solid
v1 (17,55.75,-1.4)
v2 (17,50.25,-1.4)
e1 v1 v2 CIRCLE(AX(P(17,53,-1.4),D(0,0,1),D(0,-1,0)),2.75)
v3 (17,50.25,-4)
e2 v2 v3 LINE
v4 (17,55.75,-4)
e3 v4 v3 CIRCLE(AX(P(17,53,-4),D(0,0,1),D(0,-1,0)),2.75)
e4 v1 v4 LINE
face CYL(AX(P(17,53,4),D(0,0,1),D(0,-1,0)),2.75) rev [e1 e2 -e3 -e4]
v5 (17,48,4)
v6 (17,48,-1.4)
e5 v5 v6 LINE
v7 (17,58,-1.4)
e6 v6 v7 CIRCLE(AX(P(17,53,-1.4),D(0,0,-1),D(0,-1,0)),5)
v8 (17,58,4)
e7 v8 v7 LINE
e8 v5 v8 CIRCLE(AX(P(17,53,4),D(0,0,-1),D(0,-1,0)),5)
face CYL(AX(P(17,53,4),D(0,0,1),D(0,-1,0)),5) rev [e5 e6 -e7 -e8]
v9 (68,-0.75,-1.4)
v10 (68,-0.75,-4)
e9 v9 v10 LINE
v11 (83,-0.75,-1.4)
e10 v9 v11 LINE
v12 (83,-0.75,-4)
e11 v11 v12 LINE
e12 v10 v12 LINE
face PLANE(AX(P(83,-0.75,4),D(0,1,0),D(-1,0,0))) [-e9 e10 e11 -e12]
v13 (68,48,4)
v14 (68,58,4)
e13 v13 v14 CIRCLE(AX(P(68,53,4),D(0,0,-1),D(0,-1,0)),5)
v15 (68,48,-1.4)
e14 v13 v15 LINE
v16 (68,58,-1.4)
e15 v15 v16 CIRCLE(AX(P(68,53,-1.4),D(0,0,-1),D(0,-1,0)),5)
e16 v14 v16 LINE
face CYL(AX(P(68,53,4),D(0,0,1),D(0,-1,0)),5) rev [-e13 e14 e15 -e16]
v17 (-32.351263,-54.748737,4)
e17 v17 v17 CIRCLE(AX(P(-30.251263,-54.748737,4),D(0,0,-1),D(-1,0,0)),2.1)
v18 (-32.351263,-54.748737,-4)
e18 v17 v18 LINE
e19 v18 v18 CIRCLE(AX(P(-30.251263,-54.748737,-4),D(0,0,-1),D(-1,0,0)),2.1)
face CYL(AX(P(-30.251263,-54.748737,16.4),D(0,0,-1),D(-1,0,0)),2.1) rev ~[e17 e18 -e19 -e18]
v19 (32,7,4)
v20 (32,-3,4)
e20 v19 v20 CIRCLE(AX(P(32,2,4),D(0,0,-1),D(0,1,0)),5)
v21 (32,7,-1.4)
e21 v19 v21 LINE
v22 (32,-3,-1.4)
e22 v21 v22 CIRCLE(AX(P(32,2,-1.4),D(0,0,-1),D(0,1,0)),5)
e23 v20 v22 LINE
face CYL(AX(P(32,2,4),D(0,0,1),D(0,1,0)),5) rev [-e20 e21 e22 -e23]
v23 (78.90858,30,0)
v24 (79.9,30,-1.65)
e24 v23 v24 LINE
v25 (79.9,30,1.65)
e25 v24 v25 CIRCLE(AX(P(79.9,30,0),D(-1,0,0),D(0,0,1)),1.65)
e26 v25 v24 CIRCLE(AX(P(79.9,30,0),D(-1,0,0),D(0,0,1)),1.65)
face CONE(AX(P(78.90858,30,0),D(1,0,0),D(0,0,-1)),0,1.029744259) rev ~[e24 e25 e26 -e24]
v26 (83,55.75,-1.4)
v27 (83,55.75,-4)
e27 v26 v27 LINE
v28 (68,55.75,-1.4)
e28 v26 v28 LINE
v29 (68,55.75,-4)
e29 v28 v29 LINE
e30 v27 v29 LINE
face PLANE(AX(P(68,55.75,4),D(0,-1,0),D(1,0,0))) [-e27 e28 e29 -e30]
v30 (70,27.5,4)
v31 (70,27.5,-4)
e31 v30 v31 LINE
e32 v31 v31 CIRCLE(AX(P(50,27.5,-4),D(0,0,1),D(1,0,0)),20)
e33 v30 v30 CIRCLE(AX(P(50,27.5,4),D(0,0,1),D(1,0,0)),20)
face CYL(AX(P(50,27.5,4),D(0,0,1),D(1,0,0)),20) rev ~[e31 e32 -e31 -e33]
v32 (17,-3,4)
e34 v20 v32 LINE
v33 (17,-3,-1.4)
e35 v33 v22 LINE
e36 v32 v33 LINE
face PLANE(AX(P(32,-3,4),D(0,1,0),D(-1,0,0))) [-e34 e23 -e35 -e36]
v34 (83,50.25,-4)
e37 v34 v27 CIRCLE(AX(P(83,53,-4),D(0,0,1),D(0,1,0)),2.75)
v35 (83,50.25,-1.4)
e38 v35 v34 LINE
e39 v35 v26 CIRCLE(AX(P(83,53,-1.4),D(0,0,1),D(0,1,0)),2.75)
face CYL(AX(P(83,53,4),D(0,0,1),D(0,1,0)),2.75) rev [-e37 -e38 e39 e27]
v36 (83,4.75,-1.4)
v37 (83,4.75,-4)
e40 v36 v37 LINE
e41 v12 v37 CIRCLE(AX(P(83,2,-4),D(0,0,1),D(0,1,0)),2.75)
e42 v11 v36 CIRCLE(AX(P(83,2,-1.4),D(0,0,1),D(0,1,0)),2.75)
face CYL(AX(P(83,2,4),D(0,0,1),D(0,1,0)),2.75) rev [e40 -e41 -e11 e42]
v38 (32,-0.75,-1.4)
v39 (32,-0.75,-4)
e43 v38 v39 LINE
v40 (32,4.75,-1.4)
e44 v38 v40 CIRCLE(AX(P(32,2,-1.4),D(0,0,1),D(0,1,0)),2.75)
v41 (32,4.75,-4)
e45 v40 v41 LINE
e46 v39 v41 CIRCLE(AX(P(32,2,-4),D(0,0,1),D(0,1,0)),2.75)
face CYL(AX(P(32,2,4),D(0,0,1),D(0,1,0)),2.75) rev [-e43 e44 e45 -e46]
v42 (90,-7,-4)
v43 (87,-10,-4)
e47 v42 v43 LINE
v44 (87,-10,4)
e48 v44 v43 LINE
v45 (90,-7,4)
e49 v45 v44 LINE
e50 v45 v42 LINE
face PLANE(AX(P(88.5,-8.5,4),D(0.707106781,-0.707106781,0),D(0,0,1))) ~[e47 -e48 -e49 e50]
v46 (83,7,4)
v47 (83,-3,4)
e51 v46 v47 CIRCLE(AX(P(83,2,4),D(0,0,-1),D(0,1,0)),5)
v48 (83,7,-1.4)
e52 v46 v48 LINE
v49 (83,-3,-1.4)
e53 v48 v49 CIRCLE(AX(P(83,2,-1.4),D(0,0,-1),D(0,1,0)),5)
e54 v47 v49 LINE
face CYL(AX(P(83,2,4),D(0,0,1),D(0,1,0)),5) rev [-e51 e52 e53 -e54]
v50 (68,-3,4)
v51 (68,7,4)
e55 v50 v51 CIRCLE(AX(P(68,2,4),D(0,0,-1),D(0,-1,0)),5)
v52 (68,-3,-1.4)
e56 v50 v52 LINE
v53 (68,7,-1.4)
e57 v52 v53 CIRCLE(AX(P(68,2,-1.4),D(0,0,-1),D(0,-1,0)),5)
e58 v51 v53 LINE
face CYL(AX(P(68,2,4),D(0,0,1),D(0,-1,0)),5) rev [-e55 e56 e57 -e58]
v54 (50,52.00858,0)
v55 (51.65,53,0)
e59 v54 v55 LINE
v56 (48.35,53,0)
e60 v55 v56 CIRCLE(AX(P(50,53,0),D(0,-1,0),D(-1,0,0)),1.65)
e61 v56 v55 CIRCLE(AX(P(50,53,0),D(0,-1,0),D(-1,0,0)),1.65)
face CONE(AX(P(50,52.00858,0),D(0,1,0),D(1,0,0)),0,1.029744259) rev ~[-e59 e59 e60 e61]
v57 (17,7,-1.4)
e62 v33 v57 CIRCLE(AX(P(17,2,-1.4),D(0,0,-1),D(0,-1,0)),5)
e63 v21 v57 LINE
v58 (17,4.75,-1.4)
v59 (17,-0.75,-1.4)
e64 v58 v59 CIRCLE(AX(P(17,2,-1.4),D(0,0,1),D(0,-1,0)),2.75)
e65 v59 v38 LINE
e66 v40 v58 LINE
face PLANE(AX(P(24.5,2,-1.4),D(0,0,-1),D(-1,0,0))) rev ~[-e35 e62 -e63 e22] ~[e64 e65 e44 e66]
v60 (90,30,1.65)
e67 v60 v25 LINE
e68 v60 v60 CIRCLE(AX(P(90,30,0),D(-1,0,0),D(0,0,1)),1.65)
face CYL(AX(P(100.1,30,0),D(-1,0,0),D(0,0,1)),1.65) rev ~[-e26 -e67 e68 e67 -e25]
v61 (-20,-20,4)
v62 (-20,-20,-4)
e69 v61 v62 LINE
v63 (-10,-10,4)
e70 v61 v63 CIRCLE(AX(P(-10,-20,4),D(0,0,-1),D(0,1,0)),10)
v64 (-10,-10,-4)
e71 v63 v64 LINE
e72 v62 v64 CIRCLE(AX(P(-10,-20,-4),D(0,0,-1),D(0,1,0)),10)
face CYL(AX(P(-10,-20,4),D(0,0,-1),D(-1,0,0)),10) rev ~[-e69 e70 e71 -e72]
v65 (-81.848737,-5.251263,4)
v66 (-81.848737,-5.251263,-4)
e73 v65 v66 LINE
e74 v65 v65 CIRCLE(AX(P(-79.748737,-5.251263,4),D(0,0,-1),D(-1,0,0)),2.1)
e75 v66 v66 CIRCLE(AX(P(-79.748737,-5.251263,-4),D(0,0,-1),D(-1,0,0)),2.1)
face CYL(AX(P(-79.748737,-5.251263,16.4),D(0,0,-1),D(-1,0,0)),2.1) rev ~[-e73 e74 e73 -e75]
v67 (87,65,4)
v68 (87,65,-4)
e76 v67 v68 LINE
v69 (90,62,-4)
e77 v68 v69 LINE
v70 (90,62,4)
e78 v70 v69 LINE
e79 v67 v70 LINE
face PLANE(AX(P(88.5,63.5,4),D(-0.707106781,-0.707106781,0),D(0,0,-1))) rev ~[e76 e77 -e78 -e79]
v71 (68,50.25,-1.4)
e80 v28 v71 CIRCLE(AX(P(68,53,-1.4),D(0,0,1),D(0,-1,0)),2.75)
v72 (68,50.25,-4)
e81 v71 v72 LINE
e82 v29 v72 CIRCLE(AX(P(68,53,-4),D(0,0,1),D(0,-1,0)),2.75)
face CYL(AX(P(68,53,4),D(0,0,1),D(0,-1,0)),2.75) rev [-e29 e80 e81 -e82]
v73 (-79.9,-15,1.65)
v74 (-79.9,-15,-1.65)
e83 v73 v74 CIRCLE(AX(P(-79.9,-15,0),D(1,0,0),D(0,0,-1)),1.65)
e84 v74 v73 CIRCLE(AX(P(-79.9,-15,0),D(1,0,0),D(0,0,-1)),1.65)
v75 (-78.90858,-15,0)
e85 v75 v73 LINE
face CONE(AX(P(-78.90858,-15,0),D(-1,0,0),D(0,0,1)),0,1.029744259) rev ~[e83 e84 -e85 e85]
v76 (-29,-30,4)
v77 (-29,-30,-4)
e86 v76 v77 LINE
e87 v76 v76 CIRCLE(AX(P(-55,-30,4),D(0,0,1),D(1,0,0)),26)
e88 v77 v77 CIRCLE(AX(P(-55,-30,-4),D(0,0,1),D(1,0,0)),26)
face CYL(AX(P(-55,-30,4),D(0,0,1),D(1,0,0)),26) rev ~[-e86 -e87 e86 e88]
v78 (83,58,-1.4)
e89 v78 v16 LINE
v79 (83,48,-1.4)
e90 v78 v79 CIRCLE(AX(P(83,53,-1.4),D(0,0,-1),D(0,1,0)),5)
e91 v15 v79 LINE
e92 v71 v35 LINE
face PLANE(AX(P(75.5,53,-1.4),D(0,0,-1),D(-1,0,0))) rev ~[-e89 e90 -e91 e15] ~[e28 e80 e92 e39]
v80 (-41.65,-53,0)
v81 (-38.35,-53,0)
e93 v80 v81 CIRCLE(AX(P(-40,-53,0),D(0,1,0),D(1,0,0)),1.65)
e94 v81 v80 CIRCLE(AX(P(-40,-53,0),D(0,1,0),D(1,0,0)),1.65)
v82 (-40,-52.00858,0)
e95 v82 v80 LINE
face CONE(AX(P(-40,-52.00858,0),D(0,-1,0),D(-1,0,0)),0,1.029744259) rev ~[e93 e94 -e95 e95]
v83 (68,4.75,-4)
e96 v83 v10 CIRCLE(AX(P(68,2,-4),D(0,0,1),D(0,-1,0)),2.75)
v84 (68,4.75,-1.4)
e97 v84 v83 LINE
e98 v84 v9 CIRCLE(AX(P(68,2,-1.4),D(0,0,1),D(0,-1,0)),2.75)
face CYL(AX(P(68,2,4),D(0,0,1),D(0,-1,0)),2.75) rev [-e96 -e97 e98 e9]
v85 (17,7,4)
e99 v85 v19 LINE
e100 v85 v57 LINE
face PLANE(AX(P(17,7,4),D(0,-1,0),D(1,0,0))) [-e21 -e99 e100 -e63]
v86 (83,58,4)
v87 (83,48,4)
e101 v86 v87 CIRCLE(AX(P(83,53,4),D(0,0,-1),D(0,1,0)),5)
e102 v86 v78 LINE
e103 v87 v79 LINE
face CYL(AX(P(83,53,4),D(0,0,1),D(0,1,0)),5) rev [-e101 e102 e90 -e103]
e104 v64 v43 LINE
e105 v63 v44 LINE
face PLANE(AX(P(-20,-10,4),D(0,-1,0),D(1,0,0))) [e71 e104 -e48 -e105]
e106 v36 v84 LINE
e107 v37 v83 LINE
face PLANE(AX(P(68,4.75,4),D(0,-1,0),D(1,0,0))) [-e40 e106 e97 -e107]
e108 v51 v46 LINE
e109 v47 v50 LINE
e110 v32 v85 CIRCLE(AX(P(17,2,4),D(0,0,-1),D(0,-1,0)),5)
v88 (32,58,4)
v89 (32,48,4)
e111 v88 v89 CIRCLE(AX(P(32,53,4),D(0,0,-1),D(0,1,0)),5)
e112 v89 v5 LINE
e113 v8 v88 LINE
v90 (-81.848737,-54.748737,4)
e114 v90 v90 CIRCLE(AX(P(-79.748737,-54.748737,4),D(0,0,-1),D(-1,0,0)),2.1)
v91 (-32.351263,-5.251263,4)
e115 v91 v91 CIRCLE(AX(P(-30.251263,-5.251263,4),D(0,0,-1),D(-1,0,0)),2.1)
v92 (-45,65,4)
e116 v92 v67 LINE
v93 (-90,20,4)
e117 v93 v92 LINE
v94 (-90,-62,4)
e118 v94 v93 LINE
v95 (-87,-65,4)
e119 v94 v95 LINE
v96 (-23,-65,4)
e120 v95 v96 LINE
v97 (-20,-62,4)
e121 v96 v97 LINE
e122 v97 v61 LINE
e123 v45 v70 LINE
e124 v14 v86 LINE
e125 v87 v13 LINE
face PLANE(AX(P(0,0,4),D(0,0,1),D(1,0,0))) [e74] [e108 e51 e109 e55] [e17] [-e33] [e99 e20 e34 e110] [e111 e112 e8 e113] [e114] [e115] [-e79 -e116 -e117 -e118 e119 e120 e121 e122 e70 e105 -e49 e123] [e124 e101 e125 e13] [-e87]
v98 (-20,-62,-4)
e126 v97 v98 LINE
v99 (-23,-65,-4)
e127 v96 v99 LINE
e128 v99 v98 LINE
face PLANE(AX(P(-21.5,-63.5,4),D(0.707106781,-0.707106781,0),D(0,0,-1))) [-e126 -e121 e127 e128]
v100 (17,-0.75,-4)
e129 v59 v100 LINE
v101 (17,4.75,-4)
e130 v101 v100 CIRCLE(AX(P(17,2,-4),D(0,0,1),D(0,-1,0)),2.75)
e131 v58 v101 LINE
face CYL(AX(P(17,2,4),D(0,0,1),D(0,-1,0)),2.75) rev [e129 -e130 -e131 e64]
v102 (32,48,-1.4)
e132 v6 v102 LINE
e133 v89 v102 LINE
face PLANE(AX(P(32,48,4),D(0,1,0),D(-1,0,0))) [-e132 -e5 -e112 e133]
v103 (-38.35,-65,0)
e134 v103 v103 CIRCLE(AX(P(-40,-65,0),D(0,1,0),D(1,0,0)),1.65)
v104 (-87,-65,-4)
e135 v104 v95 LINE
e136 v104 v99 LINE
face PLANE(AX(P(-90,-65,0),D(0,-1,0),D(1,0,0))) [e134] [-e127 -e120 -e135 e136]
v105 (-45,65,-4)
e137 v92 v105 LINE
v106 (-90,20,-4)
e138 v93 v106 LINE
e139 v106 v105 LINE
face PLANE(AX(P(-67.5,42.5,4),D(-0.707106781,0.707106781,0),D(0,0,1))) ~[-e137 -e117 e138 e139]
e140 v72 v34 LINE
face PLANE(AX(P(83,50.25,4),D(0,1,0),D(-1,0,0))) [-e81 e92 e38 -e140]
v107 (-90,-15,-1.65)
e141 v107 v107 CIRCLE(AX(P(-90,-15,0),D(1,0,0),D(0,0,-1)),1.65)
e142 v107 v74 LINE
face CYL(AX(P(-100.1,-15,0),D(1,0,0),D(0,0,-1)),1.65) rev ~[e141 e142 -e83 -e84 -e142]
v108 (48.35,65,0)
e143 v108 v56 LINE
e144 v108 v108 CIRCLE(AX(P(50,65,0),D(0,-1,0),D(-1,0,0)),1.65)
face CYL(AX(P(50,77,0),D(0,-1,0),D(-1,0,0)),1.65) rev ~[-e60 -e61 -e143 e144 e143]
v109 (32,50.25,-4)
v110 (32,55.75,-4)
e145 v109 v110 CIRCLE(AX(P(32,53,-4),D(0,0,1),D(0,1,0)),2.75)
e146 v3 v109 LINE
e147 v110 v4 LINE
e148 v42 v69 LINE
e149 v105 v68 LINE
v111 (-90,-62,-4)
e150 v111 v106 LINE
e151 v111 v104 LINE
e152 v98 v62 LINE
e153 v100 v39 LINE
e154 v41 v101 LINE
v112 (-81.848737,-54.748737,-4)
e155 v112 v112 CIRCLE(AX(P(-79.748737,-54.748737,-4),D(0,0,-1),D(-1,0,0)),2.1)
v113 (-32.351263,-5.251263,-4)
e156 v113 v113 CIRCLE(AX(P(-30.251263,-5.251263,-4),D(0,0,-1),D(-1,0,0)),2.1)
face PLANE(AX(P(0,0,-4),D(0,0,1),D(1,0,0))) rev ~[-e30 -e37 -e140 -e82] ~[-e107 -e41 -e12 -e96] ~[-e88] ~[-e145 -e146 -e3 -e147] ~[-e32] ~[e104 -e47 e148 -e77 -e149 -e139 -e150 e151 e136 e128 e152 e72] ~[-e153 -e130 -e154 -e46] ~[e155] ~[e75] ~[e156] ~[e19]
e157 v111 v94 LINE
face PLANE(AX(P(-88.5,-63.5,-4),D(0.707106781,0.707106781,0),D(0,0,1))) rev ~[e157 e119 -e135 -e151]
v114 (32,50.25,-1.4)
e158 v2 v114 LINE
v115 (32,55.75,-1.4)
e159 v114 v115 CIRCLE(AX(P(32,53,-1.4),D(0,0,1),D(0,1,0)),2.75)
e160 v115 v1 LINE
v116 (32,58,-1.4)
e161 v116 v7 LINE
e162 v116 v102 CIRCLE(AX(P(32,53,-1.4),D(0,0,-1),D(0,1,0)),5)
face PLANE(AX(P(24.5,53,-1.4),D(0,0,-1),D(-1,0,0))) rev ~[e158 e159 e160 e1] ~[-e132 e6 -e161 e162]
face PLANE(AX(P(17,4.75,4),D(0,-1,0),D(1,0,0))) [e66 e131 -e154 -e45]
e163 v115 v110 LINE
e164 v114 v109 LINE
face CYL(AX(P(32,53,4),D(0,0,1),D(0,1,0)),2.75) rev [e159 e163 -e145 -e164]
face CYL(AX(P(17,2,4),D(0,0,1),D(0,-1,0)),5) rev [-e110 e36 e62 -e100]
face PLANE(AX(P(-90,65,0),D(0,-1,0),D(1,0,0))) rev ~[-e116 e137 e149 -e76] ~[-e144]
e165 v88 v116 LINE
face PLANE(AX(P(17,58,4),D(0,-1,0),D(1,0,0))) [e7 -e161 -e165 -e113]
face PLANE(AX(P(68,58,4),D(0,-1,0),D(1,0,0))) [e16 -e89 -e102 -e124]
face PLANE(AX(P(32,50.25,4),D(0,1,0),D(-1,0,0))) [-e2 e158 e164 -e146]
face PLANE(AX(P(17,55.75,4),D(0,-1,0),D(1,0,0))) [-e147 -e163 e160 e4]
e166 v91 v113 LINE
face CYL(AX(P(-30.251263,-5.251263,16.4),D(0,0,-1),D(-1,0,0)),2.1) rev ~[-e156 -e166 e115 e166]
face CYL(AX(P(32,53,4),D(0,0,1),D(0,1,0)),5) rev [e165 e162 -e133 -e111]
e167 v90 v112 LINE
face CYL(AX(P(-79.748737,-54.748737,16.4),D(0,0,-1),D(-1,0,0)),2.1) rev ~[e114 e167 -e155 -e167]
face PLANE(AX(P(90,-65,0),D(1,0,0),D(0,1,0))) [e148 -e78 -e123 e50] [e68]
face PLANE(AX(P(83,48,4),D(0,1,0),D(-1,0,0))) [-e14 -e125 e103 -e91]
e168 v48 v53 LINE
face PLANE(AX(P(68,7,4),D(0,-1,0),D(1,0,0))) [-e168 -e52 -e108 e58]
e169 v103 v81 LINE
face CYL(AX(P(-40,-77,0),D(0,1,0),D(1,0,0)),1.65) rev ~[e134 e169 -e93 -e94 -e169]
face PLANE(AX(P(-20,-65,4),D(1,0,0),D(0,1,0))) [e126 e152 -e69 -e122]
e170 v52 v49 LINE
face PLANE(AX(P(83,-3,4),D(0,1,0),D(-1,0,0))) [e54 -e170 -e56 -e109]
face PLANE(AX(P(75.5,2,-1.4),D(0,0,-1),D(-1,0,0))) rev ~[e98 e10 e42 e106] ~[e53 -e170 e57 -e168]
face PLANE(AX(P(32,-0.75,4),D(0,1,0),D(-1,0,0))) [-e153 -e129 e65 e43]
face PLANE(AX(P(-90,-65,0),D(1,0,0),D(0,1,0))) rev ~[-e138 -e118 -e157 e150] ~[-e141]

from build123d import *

# Parameters (mm, degrees)
SKETCH_2_W                     = 180
SKETCH_2_H                     = 130
EXTRUDE_1_DEPTH                = 4
SKETCH_3_W                     = 110
SKETCH_3_H                     = 55
CUT_EXTRUDE_1_DEPTH            = 8
SKETCH_4_R                     = 26
CUT_EXTRUDE_2_DEPTH            = 8
HOLE_WIZARD_M5_1_D             = 4.2
HOLE_WIZARD_M5_1_DEPTH         = 12.4
HOLE_WIZARD_M5_1_TIP           = 1.2618073
SKETCH_7_R                     = 20
CUT_EXTRUDE_3_DEPTH            = 8
HOLE_WIZARD_M4_1_D             = 3.3
HOLE_WIZARD_M4_1_DEPTH         = 12
HOLE_WIZARD_M4_1_TIP           = 0.991420021
HOLE_WIZARD_M4_2_D             = 3.3
HOLE_WIZARD_M4_2_DEPTH         = 12
HOLE_WIZARD_M4_2_TIP           = 0.991420021
CHAMFER_1_SIZE                 = 45
CHAMFER_2_SIZE                 = 3
FILLET_1_R                     = 10
HOLE_WIZARD_M5_1_2_D           = 5.5
HOLE_WIZARD_M5_1_2_DEPTH       = 10.1
HOLE_WIZARD_M5_1_2_CBORE_D     = 10
HOLE_WIZARD_M5_1_2_CBORE_DEPTH = 5.4
HOLE_WIZARD_M5_1_2_TIP         = 1.652366702
CUT_EXTRUDE_6_DEPTH            = 112.30588484
CUT_EXTRUDE_7_DEPTH            = 5.4
PATTERN_LINEAR_1_COUNT         = 2
PATTERN_LINEAR_1_PITCH         = 51
PATTERN_LINEAR_1_COUNT_DIR2    = 2
PATTERN_LINEAR_1_PITCH_DIR2    = 51
HOLE_WIZARD_M4_3_D             = 3.3
HOLE_WIZARD_M4_3_DEPTH         = 10.1
HOLE_WIZARD_M4_3_TIP           = 0.991420021
HOLE_WIZARD_M4_4_D             = 3.3
HOLE_WIZARD_M4_4_DEPTH         = 10.1
HOLE_WIZARD_M4_4_TIP           = 0.991420021


with BuildPart() as part:
    # 草图2 → 凸台-拉伸1 (new, symmetric)
    with BuildSketch(Plane.XY):
        Rectangle(SKETCH_2_W, SKETCH_2_H)
    extrude(amount=EXTRUDE_1_DEPTH, both=True)

    # 草图3 → 切除-拉伸1 (cut)
    with BuildSketch(Plane.XY.offset(4)):
        with Locations((35, -37.5)):
            Rectangle(SKETCH_3_W, SKETCH_3_H)
    extrude(amount=-CUT_EXTRUDE_1_DEPTH, mode=Mode.SUBTRACT)

    # 草图4 → 切除-拉伸2 (cut)
    with BuildSketch(Plane.XY.offset(4)):
        with Locations((-55, -30)):
            Circle(SKETCH_4_R)
    extrude(amount=-CUT_EXTRUDE_2_DEPTH, mode=Mode.SUBTRACT)

    # Hole Wizard M5 _1
    with Locations(Plane.XY.offset(4)):
        with Locations((-30.251262658, -54.748737342), (-79.748737342, -5.251262658), (-79.748737342, -54.748737342), (-30.251262658, -5.251262658)):
            Hole(HOLE_WIZARD_M5_1_D / 2, depth=HOLE_WIZARD_M5_1_DEPTH)
            with Locations((0, 0, -(HOLE_WIZARD_M5_1_DEPTH + HOLE_WIZARD_M5_1_TIP / 2))):  # 118° drill point
                Cone(0, HOLE_WIZARD_M5_1_D / 2, HOLE_WIZARD_M5_1_TIP, mode=Mode.SUBTRACT)

    # 草图7 → 切除-拉伸3 (cut)
    with BuildSketch(Plane.XY.offset(4)):
        with Locations((50, 27.5)):
            Circle(SKETCH_7_R)
    extrude(amount=-CUT_EXTRUDE_3_DEPTH, mode=Mode.SUBTRACT)

    # M4 螺纹孔1
    with Locations(Plane(origin=(0, 65, 0), x_dir=(1, 0, 0), z_dir=(0, 1, 0))):
        with Locations((50, 0)):
            Hole(HOLE_WIZARD_M4_1_D / 2, depth=HOLE_WIZARD_M4_1_DEPTH)
            with Locations((0, 0, -(HOLE_WIZARD_M4_1_DEPTH + HOLE_WIZARD_M4_1_TIP / 2))):  # 118° drill point
                Cone(0, HOLE_WIZARD_M4_1_D / 2, HOLE_WIZARD_M4_1_TIP, mode=Mode.SUBTRACT)

    # M4 螺纹孔2
    with Locations(Plane(origin=(0, -65, 0), x_dir=(-1, 0, 0), z_dir=(0, -1, 0))):
        with Locations((40, 0)):
            Hole(HOLE_WIZARD_M4_2_D / 2, depth=HOLE_WIZARD_M4_2_DEPTH)
            with Locations((0, 0, -(HOLE_WIZARD_M4_2_DEPTH + HOLE_WIZARD_M4_2_TIP / 2))):  # 118° drill point
                Cone(0, HOLE_WIZARD_M4_2_D / 2, HOLE_WIZARD_M4_2_TIP, mode=Mode.SUBTRACT)

    # 倒角1
    chamfer_1_edges = [part.edges().sort_by_distance(p)[0] for p in [
        (-90, 65, 0),
    ]]
    chamfer(chamfer_1_edges, length=CHAMFER_1_SIZE)

    # 倒角2
    chamfer_2_edges = [part.edges().sort_by_distance(p)[0] for p in [
        (90, -10, 0),
        (-20, -65, 0),
        (-90, -65, 0),
        (90, 65, 0),
    ]]
    chamfer(chamfer_2_edges, length=CHAMFER_2_SIZE)

    # 圆角1
    fillet_1_edges = [part.edges().sort_by_distance(p)[0] for p in [
        (-20, -10, 0),
    ]]
    fillet(fillet_1_edges, radius=FILLET_1_R)

    # Hole Wizard M5 _1 2
    with Locations(Plane.XY.offset(4)):
        with Locations((24.5, 53), (75.5, 53), (24.5, 2), (75.5, 2)):
            CounterBoreHole(HOLE_WIZARD_M5_1_2_D / 2, HOLE_WIZARD_M5_1_2_CBORE_D / 2, HOLE_WIZARD_M5_1_2_CBORE_DEPTH, depth=HOLE_WIZARD_M5_1_2_DEPTH)
            with Locations((0, 0, -(HOLE_WIZARD_M5_1_2_DEPTH + HOLE_WIZARD_M5_1_2_TIP / 2))):  # 118° drill point
                Cone(0, HOLE_WIZARD_M5_1_2_D / 2, HOLE_WIZARD_M5_1_2_TIP, mode=Mode.SUBTRACT)

    # 草图18 → 切除-拉伸6 (cut, through all)
    with BuildSketch(Plane.XY.offset(4)):
        with BuildLine():
            Line((17, 55.75), (32, 55.75))
            ThreePointArc((32, 55.75), (34.75, 53), (32, 50.25))
            Line((32, 50.25), (17, 50.25))
            ThreePointArc((17, 50.25), (14.25, 53), (17, 55.75))
        make_face()
    cut_extrude_6 = extrude(amount=-CUT_EXTRUDE_6_DEPTH, mode=Mode.SUBTRACT)

    # 草图19 → 切除-拉伸7 (cut)
    with BuildSketch(Plane.XY.offset(4)):
        with BuildLine():
            Line((17, 58), (32, 58))
            ThreePointArc((32, 58), (37, 53), (32, 48))
            Line((32, 48), (17, 48))
            ThreePointArc((17, 48), (12, 53), (17, 58))
        make_face()
    cut_extrude_7 = extrude(amount=-CUT_EXTRUDE_7_DEPTH, mode=Mode.SUBTRACT)

    # 阵列(线性)1: 切除-拉伸6, Cut-Extrude 7 2 × 2
    with Locations(*[(i * PATTERN_LINEAR_1_PITCH, -j * PATTERN_LINEAR_1_PITCH_DIR2, 0) for i in range(PATTERN_LINEAR_1_COUNT) for j in range(PATTERN_LINEAR_1_COUNT_DIR2) if (i, j) != (0, 0)]):
        add(cut_extrude_6, mode=Mode.SUBTRACT)
        add(cut_extrude_7, mode=Mode.SUBTRACT)

    # M4 螺纹孔3
    with Locations(Plane.ZY.offset(90)):
        with Locations((0, -15)):
            Hole(HOLE_WIZARD_M4_3_D / 2, depth=HOLE_WIZARD_M4_3_DEPTH)
            with Locations((0, 0, -(HOLE_WIZARD_M4_3_DEPTH + HOLE_WIZARD_M4_3_TIP / 2))):  # 118° drill point
                Cone(0, HOLE_WIZARD_M4_3_D / 2, HOLE_WIZARD_M4_3_TIP, mode=Mode.SUBTRACT)

    # M4 螺纹孔4
    with Locations(Plane(origin=(90, 0, 0), x_dir=(0, 0, -1), z_dir=(1, 0, 0))):
        with Locations((0, 30)):
            Hole(HOLE_WIZARD_M4_4_D / 2, depth=HOLE_WIZARD_M4_4_DEPTH)
            with Locations((0, 0, -(HOLE_WIZARD_M4_4_DEPTH + HOLE_WIZARD_M4_4_TIP / 2))):  # 118° drill point
                Cone(0, HOLE_WIZARD_M4_4_D / 2, HOLE_WIZARD_M4_4_TIP, mode=Mode.SUBTRACT)


solid = part.part
